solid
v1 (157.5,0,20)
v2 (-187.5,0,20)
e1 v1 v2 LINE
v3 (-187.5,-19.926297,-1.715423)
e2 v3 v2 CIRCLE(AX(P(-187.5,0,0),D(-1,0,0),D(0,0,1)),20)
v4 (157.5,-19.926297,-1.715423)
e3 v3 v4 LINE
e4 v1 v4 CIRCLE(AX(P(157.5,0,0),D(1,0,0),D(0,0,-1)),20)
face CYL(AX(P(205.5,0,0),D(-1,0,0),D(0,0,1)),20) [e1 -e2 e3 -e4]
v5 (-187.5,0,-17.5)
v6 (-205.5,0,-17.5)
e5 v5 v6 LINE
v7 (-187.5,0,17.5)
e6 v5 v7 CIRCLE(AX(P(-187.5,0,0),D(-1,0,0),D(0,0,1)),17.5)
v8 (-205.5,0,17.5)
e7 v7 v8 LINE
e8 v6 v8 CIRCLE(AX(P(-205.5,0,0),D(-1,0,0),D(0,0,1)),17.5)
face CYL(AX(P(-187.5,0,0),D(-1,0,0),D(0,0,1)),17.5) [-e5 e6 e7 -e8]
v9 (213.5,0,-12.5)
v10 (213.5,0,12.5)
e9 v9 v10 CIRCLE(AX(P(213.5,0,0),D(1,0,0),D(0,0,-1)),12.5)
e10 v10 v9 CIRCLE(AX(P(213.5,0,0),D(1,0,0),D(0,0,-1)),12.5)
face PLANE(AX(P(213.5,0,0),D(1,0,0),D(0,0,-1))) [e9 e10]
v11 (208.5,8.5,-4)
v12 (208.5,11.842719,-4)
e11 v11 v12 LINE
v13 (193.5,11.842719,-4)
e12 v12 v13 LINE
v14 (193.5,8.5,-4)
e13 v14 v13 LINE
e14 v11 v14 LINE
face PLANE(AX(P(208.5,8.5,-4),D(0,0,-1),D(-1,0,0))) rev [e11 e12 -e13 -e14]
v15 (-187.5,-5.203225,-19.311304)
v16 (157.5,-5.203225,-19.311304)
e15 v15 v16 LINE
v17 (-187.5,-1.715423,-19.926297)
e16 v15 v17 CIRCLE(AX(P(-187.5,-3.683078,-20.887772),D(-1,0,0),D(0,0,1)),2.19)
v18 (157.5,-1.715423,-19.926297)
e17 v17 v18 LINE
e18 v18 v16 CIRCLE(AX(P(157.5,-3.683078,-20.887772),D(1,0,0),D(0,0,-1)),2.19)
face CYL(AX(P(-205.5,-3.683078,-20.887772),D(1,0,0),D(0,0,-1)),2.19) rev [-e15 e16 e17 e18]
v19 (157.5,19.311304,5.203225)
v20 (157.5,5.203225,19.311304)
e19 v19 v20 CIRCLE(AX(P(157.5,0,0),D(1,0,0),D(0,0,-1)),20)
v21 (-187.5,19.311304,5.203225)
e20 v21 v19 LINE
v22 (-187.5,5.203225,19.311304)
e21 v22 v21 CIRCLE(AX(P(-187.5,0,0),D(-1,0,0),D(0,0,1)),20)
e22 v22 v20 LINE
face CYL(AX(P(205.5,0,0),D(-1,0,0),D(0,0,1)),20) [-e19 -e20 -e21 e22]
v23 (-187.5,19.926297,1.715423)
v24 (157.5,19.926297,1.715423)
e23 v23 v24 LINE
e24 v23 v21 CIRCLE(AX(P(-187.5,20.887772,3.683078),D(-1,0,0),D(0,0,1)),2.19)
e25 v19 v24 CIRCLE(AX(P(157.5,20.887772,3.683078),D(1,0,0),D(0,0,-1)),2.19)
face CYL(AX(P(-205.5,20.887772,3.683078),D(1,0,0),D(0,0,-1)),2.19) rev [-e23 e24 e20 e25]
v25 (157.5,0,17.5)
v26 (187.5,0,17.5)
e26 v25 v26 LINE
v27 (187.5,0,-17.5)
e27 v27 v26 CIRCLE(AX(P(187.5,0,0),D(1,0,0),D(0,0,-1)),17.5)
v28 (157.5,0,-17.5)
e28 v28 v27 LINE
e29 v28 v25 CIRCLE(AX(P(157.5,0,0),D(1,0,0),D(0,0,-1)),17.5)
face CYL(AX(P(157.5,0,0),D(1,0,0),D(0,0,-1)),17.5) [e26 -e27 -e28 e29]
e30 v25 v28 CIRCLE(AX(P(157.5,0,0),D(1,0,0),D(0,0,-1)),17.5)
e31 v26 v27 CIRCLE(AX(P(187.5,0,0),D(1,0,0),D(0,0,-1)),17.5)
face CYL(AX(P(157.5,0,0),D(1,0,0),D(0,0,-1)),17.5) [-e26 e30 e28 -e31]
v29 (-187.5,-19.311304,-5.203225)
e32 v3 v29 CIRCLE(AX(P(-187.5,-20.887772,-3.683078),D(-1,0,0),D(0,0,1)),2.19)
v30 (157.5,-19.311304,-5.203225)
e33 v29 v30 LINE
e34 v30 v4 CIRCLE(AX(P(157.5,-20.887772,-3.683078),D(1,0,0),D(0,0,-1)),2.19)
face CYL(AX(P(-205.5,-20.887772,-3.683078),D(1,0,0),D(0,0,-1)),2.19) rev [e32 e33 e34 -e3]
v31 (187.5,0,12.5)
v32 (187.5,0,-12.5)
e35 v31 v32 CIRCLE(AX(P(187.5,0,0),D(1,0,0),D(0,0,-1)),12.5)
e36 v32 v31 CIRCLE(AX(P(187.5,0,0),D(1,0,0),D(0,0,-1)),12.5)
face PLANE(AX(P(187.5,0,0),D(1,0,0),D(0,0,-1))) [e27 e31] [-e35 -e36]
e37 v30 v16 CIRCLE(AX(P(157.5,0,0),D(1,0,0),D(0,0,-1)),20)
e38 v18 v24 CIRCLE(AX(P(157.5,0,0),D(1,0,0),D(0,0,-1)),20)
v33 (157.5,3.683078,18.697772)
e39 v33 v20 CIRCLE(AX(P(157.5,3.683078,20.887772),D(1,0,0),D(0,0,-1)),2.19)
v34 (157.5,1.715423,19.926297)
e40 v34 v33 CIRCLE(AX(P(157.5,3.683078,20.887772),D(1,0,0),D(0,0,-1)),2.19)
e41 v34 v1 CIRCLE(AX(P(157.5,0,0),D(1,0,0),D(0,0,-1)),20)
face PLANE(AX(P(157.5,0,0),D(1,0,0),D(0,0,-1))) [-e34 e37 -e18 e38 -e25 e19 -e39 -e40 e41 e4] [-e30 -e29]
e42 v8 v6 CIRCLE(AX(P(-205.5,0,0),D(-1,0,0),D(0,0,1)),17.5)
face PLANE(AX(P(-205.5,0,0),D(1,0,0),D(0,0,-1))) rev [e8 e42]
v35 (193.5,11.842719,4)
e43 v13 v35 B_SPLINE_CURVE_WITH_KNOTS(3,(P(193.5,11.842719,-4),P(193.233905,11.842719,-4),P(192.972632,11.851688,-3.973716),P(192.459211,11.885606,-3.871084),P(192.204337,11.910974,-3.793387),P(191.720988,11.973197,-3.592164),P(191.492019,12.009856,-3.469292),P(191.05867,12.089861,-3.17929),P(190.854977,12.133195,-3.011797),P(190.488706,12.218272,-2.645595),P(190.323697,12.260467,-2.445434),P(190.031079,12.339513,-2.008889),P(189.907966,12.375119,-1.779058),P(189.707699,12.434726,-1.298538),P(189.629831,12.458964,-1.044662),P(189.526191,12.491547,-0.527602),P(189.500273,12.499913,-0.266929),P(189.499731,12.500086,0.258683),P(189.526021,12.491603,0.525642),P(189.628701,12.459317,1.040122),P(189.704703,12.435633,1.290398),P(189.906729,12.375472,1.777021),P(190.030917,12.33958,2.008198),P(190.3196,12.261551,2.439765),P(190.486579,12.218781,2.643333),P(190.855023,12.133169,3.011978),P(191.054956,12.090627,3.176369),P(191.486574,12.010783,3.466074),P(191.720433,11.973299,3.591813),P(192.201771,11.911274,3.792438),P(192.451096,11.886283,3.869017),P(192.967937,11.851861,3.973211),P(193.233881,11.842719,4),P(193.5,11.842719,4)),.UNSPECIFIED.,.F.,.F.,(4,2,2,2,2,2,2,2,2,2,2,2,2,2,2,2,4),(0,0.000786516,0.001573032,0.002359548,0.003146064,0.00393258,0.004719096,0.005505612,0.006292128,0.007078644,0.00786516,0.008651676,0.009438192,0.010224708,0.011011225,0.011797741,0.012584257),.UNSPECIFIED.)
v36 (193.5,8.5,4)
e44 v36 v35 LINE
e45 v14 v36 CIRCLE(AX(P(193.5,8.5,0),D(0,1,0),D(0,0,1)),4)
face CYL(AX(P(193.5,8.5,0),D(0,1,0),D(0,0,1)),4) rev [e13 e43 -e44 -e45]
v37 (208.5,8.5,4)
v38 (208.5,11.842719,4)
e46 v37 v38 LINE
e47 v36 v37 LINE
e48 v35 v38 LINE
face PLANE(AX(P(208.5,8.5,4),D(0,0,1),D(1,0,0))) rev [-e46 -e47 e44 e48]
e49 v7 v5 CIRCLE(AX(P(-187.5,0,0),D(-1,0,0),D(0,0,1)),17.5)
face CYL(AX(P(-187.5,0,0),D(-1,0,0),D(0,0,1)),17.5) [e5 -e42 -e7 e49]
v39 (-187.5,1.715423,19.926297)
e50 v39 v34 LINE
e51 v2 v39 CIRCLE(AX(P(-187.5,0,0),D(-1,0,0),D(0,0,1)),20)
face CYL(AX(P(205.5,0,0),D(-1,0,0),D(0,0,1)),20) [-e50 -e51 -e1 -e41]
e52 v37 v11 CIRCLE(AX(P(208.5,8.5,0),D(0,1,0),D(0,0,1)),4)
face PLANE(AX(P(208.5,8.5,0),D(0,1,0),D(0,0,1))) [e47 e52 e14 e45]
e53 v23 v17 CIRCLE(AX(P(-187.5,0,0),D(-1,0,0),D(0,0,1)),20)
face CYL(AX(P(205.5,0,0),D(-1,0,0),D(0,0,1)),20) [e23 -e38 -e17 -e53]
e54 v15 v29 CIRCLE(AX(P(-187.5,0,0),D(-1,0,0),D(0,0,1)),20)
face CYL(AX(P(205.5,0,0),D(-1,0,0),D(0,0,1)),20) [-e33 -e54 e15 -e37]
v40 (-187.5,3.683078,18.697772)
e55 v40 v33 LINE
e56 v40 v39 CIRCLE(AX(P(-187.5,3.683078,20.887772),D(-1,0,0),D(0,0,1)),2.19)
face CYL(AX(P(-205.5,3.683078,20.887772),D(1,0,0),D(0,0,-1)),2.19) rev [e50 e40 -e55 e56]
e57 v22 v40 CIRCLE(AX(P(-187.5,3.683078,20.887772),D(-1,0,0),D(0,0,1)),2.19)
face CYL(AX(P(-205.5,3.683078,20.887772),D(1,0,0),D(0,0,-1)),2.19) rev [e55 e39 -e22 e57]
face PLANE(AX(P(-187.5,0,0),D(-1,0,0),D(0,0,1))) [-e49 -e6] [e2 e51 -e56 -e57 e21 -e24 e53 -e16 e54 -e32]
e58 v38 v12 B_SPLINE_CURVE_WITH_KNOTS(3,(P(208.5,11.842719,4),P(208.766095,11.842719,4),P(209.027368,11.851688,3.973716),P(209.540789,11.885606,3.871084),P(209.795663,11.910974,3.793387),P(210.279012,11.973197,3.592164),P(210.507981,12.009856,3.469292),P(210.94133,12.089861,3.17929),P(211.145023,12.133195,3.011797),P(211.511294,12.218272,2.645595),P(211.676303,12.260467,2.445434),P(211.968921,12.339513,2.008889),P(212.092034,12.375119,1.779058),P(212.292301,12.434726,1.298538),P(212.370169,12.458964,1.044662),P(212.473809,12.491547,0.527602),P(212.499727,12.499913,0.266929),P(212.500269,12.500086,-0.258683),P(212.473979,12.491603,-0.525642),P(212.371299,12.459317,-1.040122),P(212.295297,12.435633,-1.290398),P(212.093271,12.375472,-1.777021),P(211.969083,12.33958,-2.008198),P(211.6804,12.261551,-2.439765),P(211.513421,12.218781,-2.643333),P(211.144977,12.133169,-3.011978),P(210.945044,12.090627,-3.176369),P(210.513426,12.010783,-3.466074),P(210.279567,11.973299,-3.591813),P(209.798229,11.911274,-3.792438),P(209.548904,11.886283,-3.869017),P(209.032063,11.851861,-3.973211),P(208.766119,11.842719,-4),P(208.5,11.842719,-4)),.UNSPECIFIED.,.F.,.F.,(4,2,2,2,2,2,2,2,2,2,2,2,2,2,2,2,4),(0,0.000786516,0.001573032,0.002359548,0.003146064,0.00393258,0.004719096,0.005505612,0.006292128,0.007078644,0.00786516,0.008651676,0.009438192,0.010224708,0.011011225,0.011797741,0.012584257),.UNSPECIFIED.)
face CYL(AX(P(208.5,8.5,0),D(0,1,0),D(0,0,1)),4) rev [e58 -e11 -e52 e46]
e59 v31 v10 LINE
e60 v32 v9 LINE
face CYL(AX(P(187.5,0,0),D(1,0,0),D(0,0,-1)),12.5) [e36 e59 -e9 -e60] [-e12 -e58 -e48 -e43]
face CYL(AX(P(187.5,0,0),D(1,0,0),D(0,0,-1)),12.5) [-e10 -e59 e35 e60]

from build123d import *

# Parameters (mm, degrees)
CUT_EXTRUDE_1_DEPTH      = 205.5
CUT_EXTRUDE_1_DEPTH_BACK = 205.5
SKETCH_2_R               = 40
SKETCH_3_OUTSIDE_W       = 124.974
SKETCH_3_OUTSIDE_H       = 124.974
SKETCH_3_OUTSIDE_R       = 17.5
CUT_EXTRUDE_2_DEPTH      = 18
SKETCH_4_OUTSIDE_W       = 124.974
SKETCH_4_OUTSIDE_H       = 124.974
SKETCH_4_OUTSIDE_R       = 12.5
CUT_EXTRUDE_3_DEPTH      = 18
SKETCH_5_OUTSIDE_W       = 124.974
SKETCH_5_OUTSIDE_H       = 124.974
SKETCH_5_OUTSIDE_R       = 17.5
CUT_EXTRUDE_4_DEPTH      = 30
EXTRUDE_START            = 8
SKETCH_7_R               = 12.5
EXTRUDE_1_DEPTH          = 8
CUT_EXTRUDE_5_DEPTH      = 4


with BuildPart() as part:
    # 草图1 → 旋转1 (revolve)
    with BuildSketch(Plane.XY, mode=Mode.PRIVATE) as revolve_1_sk:
        Polygon((-205.5, 0), (-205.5, 19), (-204.5, 20), (204.5, 20), (205.5, 19), (205.5, 0), align=None)
    revolve(revolve_1_sk.sketch.rotate(Axis((205.5, 0, 0), (-1, 0, 0)), 270), axis=Axis((205.5, 0, 0), (-1, 0, 0)))

    # 草图2 → 切除-拉伸1 (cut, two sides: drawn at the far end of the back side and taken through both)
    with BuildSketch(Plane(origin=(0, 0, 0), x_dir=(0, 0, -1), z_dir=(1, 0, 0)).offset(-CUT_EXTRUDE_1_DEPTH_BACK)):
        Circle(SKETCH_2_R)
        with BuildLine():
            ThreePointArc((-19.926297295, 1.715423015), (-14.142135624, -14.142135624), (1.715423015, -19.926297295))
            ThreePointArc((1.715423015, -19.926297295), (3.302788339, -18.731043462), (5.203224708, -19.311303753))
            ThreePointArc((5.203224708, -19.311303753), (14.142135624, -14.142135624), (19.311303753, -5.203224708))
            ThreePointArc((19.311303753, -5.203224708), (18.731043462, -3.302788339), (19.926297295, -1.715423015))
            ThreePointArc((19.926297295, -1.715423015), (14.142135624, 14.142135624), (-1.715423015, 19.926297295))
            ThreePointArc((-1.715423015, 19.926297295), (-3.302788339, 18.731043462), (-5.203224708, 19.311303753))
            ThreePointArc((-5.203224708, 19.311303753), (-14.142135624, 14.142135624), (-19.311303753, 5.203224708))
            ThreePointArc((-19.311303753, 5.203224708), (-18.731043462, 3.302788339), (-19.926297295, 1.715423015))
        make_face(mode=Mode.SUBTRACT)
    extrude(amount=CUT_EXTRUDE_1_DEPTH + CUT_EXTRUDE_1_DEPTH_BACK, mode=Mode.SUBTRACT)

    # 草图3 outside → 切除-拉伸2 (cut)
    with BuildSketch(Plane.ZY.offset(205.5)):
        Rectangle(SKETCH_3_OUTSIDE_W, SKETCH_3_OUTSIDE_H)
        Circle(SKETCH_3_OUTSIDE_R, mode=Mode.SUBTRACT)
    extrude(amount=-CUT_EXTRUDE_2_DEPTH, mode=Mode.SUBTRACT)

    # 草图4 outside → 切除-拉伸3 (cut)
    with BuildSketch(Plane(origin=(205.5, 0, 0), x_dir=(0, 0, -1), z_dir=(1, 0, 0))):
        Rectangle(SKETCH_4_OUTSIDE_W, SKETCH_4_OUTSIDE_H)
        Circle(SKETCH_4_OUTSIDE_R, mode=Mode.SUBTRACT)
    extrude(amount=-CUT_EXTRUDE_3_DEPTH, mode=Mode.SUBTRACT)

    # 草图5 outside → 切除-拉伸4 (cut)
    with BuildSketch(Plane(origin=(187.5, 0, 0), x_dir=(0, 0, -1), z_dir=(1, 0, 0))):
        Rectangle(SKETCH_5_OUTSIDE_W, SKETCH_5_OUTSIDE_H)
        with Locations(Location((0, 0, 0), (0, 0, 180))):
            Circle(SKETCH_5_OUTSIDE_R, mode=Mode.SUBTRACT)
    extrude(amount=-CUT_EXTRUDE_4_DEPTH, mode=Mode.SUBTRACT)

    # 草图7 → 凸台-拉伸1 (add)
    with BuildSketch(Plane(origin=(205.5, 0, 0), x_dir=(0, 0, -1), z_dir=(1, 0, 0)).offset(EXTRUDE_START)):
        Circle(SKETCH_7_R)
    extrude(amount=-EXTRUDE_1_DEPTH)

    # 草图6 → 切除-拉伸5 (cut)
    with BuildSketch(Plane(origin=(0, 12.5, 0), x_dir=(1, 0, 0), z_dir=(0, 1, 0))):
        with BuildLine():
            Line((208.5, -4), (193.5, -4))
            ThreePointArc((193.5, -4), (189.5, 0), (193.5, 4))
            Line((193.5, 4), (208.5, 4))
            ThreePointArc((208.5, 4), (212.5, 0), (208.5, -4))
        make_face()
    extrude(amount=-CUT_EXTRUDE_5_DEPTH, mode=Mode.SUBTRACT)


solid = part.part
